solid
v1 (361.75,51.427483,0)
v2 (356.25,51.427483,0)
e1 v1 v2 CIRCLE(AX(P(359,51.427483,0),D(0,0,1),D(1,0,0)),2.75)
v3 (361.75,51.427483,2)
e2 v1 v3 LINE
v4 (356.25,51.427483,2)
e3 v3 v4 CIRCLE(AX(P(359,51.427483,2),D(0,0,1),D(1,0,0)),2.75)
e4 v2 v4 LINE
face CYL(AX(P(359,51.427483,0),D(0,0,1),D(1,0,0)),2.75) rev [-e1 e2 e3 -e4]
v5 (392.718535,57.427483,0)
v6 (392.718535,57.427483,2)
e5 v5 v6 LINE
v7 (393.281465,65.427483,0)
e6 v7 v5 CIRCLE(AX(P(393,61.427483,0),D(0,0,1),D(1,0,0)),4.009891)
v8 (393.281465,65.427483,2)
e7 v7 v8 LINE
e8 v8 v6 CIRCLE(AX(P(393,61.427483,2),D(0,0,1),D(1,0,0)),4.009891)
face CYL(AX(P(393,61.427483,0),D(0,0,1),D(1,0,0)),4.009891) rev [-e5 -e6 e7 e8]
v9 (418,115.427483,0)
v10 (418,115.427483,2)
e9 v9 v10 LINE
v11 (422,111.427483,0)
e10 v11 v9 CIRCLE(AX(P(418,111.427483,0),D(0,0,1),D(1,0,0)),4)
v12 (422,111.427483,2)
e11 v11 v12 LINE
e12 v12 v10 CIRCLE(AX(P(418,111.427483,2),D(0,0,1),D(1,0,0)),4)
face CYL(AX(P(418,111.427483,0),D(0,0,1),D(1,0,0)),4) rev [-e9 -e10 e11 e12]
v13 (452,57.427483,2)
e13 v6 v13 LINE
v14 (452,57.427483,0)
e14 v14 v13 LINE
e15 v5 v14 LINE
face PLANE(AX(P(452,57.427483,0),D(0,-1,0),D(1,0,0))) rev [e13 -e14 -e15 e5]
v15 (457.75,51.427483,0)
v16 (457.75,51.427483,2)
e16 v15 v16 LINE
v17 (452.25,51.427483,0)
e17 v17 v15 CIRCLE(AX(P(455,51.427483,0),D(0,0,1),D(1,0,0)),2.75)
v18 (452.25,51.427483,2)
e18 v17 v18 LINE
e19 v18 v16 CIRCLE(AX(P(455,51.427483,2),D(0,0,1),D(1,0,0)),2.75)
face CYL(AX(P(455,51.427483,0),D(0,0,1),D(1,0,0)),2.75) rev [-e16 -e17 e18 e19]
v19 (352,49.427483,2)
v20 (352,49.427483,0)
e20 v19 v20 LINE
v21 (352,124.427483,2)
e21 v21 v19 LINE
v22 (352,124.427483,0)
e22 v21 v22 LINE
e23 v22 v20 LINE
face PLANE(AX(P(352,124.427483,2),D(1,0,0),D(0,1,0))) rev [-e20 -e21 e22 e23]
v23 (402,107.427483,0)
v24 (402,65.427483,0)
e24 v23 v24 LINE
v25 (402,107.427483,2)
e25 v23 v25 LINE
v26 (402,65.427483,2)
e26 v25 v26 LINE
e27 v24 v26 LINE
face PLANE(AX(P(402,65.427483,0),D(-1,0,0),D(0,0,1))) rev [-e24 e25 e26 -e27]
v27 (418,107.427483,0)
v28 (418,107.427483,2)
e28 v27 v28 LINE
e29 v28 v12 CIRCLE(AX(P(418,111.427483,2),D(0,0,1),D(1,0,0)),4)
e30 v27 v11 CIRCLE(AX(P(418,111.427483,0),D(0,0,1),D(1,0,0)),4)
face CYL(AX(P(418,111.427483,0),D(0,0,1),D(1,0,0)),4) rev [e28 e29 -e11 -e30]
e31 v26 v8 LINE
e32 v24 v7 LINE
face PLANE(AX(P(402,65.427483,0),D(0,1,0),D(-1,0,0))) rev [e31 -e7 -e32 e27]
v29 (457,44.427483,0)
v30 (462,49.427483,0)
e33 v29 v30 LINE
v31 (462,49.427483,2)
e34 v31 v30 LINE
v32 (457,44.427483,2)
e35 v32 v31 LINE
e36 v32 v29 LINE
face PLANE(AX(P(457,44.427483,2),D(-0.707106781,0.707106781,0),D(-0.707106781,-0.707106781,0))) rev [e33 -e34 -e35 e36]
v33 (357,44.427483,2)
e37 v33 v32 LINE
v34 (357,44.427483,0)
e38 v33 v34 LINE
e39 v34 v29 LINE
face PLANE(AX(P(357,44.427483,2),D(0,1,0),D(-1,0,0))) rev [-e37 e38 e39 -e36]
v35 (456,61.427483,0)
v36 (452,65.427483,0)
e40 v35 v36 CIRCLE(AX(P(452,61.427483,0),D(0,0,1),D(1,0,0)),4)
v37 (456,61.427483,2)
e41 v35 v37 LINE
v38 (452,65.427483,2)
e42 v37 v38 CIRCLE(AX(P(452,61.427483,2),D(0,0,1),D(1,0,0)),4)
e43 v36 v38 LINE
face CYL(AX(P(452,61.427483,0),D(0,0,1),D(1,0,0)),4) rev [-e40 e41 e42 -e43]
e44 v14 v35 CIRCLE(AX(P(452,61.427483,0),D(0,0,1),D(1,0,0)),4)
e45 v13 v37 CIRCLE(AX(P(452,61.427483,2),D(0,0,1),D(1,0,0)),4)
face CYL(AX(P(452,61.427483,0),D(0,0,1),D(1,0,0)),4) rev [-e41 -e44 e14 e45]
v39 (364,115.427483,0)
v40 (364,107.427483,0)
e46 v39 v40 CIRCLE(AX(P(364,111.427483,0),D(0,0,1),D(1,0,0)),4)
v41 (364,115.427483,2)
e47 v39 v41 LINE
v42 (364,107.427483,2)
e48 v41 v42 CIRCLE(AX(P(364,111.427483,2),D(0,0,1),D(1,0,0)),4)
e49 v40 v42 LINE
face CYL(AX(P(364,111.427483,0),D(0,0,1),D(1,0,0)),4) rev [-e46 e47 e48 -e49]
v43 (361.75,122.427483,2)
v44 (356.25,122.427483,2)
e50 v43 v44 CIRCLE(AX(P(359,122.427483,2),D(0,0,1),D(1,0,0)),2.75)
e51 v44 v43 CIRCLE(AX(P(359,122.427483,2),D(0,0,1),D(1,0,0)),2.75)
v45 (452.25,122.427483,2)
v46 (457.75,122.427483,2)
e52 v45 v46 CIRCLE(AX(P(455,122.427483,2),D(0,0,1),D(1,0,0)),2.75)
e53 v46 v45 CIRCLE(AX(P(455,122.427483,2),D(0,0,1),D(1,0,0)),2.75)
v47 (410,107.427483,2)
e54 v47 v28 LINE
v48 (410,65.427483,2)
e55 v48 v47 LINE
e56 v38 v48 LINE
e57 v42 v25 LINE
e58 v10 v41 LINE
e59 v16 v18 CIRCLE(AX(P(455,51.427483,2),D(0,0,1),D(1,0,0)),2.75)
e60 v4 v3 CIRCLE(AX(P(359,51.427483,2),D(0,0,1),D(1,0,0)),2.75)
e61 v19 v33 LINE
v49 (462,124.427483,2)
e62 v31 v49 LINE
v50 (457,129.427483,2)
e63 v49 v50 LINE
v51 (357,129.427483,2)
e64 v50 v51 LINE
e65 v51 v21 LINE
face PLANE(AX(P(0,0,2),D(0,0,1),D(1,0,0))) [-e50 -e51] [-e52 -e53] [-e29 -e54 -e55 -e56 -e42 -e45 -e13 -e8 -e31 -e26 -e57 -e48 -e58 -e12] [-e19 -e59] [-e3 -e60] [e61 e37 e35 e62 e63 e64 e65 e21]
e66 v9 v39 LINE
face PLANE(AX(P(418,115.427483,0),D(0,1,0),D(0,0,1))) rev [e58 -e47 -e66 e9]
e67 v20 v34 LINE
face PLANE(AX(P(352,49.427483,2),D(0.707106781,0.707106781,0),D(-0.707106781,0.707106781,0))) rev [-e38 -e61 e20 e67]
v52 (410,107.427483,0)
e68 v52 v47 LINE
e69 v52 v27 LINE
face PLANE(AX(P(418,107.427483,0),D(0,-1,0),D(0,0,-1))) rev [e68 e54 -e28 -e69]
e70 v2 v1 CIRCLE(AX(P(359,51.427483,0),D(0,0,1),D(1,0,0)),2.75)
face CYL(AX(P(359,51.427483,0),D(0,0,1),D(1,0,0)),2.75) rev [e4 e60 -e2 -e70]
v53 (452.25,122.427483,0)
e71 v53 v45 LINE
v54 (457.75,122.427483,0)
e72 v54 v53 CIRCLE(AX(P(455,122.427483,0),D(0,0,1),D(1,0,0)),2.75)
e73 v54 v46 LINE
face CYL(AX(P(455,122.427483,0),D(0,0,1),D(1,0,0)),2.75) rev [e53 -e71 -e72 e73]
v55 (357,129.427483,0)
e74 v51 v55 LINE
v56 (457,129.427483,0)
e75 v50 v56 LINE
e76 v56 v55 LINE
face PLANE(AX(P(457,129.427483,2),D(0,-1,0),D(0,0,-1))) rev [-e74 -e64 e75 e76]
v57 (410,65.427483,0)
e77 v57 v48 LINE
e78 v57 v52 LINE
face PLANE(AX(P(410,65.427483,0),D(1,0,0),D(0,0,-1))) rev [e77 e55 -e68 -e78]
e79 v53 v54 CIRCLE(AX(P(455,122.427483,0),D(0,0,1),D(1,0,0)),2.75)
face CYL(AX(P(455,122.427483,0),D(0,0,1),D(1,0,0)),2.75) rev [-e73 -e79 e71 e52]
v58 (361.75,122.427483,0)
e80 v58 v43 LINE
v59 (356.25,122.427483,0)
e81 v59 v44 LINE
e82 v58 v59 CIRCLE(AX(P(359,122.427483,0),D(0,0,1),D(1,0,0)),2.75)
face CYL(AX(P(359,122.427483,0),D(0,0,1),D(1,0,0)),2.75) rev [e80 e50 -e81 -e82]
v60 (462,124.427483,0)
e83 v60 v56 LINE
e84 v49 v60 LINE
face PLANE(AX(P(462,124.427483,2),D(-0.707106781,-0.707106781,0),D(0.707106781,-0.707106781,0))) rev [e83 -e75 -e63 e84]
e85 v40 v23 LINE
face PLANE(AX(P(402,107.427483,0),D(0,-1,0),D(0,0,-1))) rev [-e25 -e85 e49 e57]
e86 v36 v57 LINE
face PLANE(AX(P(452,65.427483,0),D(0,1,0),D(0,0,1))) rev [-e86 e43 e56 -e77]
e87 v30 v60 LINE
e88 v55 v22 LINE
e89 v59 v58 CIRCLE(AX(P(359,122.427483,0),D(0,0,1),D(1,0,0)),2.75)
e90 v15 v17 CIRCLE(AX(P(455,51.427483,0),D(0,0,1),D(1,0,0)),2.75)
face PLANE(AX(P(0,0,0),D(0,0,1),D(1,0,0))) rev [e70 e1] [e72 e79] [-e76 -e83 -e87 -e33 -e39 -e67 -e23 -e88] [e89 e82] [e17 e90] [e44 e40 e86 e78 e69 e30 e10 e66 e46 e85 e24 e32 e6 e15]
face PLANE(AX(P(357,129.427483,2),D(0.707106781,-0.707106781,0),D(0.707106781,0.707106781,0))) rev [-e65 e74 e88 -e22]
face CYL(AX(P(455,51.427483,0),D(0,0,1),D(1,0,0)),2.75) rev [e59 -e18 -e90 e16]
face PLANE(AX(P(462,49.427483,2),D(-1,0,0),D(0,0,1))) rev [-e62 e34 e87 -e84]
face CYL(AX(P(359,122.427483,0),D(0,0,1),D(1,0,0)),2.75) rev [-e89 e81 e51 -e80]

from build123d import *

# Parameters (mm, degrees)
EXTRUDE_1_DEPTH     = 2
CUT_EXTRUDE_1_DEPTH = 2
SKETCH_3_R          = 2.75
CUT_EXTRUDE_2_DEPTH = 2


with BuildPart() as part:
    # 草图1 → 凸台-拉伸1 (new body)
    with BuildSketch(Plane.XY):
        Polygon((357, 44.4274829), (457, 44.4274829), (462, 49.4274829), (462, 124.4274829), (457, 129.4274829), (357, 129.4274829), (352, 124.4274829), (352, 49.4274829), align=None)
    extrude(amount=EXTRUDE_1_DEPTH)

    # 草图2 → 切除-拉伸1 (cut)
    with BuildSketch(Plane.XY.offset(2)):
        with BuildLine():
            Line((452, 57.4274829), (392.718534883, 57.4274829))
            ThreePointArc((392.718534883, 57.4274829), (389, 61.708948017), (393.281465117, 65.4274829))
            Line((393.281465117, 65.4274829), (402, 65.4274829))
            Line((402, 65.4274829), (402, 107.4274829))
            Line((402, 107.4274829), (364, 107.4274829))
            ThreePointArc((364, 107.4274829), (360, 111.4274829), (364, 115.4274829))
            Line((364, 115.4274829), (418, 115.4274829))
            ThreePointArc((418, 115.4274829), (422, 111.4274829), (418, 107.4274829))
            Line((418, 107.4274829), (410, 107.4274829))
            Line((410, 107.4274829), (410, 65.4274829))
            Line((410, 65.4274829), (452, 65.4274829))
            ThreePointArc((452, 65.4274829), (456, 61.4274829), (452, 57.4274829))
        make_face()
    extrude(amount=-CUT_EXTRUDE_1_DEPTH, mode=Mode.SUBTRACT)

    # 草图3 → 切除-拉伸2 (cut)
    with BuildSketch(Plane.XY.offset(2)):
        with Locations((455, 51.4274829)):
            Circle(SKETCH_3_R)
        with Locations((359, 51.4274829)):
            Circle(SKETCH_3_R)
        with Locations((455, 122.4274829)):
            Circle(SKETCH_3_R)
        with Locations((359, 122.4274829)):
            Circle(SKETCH_3_R)
    extrude(amount=-CUT_EXTRUDE_2_DEPTH, mode=Mode.SUBTRACT)


solid = part.part
